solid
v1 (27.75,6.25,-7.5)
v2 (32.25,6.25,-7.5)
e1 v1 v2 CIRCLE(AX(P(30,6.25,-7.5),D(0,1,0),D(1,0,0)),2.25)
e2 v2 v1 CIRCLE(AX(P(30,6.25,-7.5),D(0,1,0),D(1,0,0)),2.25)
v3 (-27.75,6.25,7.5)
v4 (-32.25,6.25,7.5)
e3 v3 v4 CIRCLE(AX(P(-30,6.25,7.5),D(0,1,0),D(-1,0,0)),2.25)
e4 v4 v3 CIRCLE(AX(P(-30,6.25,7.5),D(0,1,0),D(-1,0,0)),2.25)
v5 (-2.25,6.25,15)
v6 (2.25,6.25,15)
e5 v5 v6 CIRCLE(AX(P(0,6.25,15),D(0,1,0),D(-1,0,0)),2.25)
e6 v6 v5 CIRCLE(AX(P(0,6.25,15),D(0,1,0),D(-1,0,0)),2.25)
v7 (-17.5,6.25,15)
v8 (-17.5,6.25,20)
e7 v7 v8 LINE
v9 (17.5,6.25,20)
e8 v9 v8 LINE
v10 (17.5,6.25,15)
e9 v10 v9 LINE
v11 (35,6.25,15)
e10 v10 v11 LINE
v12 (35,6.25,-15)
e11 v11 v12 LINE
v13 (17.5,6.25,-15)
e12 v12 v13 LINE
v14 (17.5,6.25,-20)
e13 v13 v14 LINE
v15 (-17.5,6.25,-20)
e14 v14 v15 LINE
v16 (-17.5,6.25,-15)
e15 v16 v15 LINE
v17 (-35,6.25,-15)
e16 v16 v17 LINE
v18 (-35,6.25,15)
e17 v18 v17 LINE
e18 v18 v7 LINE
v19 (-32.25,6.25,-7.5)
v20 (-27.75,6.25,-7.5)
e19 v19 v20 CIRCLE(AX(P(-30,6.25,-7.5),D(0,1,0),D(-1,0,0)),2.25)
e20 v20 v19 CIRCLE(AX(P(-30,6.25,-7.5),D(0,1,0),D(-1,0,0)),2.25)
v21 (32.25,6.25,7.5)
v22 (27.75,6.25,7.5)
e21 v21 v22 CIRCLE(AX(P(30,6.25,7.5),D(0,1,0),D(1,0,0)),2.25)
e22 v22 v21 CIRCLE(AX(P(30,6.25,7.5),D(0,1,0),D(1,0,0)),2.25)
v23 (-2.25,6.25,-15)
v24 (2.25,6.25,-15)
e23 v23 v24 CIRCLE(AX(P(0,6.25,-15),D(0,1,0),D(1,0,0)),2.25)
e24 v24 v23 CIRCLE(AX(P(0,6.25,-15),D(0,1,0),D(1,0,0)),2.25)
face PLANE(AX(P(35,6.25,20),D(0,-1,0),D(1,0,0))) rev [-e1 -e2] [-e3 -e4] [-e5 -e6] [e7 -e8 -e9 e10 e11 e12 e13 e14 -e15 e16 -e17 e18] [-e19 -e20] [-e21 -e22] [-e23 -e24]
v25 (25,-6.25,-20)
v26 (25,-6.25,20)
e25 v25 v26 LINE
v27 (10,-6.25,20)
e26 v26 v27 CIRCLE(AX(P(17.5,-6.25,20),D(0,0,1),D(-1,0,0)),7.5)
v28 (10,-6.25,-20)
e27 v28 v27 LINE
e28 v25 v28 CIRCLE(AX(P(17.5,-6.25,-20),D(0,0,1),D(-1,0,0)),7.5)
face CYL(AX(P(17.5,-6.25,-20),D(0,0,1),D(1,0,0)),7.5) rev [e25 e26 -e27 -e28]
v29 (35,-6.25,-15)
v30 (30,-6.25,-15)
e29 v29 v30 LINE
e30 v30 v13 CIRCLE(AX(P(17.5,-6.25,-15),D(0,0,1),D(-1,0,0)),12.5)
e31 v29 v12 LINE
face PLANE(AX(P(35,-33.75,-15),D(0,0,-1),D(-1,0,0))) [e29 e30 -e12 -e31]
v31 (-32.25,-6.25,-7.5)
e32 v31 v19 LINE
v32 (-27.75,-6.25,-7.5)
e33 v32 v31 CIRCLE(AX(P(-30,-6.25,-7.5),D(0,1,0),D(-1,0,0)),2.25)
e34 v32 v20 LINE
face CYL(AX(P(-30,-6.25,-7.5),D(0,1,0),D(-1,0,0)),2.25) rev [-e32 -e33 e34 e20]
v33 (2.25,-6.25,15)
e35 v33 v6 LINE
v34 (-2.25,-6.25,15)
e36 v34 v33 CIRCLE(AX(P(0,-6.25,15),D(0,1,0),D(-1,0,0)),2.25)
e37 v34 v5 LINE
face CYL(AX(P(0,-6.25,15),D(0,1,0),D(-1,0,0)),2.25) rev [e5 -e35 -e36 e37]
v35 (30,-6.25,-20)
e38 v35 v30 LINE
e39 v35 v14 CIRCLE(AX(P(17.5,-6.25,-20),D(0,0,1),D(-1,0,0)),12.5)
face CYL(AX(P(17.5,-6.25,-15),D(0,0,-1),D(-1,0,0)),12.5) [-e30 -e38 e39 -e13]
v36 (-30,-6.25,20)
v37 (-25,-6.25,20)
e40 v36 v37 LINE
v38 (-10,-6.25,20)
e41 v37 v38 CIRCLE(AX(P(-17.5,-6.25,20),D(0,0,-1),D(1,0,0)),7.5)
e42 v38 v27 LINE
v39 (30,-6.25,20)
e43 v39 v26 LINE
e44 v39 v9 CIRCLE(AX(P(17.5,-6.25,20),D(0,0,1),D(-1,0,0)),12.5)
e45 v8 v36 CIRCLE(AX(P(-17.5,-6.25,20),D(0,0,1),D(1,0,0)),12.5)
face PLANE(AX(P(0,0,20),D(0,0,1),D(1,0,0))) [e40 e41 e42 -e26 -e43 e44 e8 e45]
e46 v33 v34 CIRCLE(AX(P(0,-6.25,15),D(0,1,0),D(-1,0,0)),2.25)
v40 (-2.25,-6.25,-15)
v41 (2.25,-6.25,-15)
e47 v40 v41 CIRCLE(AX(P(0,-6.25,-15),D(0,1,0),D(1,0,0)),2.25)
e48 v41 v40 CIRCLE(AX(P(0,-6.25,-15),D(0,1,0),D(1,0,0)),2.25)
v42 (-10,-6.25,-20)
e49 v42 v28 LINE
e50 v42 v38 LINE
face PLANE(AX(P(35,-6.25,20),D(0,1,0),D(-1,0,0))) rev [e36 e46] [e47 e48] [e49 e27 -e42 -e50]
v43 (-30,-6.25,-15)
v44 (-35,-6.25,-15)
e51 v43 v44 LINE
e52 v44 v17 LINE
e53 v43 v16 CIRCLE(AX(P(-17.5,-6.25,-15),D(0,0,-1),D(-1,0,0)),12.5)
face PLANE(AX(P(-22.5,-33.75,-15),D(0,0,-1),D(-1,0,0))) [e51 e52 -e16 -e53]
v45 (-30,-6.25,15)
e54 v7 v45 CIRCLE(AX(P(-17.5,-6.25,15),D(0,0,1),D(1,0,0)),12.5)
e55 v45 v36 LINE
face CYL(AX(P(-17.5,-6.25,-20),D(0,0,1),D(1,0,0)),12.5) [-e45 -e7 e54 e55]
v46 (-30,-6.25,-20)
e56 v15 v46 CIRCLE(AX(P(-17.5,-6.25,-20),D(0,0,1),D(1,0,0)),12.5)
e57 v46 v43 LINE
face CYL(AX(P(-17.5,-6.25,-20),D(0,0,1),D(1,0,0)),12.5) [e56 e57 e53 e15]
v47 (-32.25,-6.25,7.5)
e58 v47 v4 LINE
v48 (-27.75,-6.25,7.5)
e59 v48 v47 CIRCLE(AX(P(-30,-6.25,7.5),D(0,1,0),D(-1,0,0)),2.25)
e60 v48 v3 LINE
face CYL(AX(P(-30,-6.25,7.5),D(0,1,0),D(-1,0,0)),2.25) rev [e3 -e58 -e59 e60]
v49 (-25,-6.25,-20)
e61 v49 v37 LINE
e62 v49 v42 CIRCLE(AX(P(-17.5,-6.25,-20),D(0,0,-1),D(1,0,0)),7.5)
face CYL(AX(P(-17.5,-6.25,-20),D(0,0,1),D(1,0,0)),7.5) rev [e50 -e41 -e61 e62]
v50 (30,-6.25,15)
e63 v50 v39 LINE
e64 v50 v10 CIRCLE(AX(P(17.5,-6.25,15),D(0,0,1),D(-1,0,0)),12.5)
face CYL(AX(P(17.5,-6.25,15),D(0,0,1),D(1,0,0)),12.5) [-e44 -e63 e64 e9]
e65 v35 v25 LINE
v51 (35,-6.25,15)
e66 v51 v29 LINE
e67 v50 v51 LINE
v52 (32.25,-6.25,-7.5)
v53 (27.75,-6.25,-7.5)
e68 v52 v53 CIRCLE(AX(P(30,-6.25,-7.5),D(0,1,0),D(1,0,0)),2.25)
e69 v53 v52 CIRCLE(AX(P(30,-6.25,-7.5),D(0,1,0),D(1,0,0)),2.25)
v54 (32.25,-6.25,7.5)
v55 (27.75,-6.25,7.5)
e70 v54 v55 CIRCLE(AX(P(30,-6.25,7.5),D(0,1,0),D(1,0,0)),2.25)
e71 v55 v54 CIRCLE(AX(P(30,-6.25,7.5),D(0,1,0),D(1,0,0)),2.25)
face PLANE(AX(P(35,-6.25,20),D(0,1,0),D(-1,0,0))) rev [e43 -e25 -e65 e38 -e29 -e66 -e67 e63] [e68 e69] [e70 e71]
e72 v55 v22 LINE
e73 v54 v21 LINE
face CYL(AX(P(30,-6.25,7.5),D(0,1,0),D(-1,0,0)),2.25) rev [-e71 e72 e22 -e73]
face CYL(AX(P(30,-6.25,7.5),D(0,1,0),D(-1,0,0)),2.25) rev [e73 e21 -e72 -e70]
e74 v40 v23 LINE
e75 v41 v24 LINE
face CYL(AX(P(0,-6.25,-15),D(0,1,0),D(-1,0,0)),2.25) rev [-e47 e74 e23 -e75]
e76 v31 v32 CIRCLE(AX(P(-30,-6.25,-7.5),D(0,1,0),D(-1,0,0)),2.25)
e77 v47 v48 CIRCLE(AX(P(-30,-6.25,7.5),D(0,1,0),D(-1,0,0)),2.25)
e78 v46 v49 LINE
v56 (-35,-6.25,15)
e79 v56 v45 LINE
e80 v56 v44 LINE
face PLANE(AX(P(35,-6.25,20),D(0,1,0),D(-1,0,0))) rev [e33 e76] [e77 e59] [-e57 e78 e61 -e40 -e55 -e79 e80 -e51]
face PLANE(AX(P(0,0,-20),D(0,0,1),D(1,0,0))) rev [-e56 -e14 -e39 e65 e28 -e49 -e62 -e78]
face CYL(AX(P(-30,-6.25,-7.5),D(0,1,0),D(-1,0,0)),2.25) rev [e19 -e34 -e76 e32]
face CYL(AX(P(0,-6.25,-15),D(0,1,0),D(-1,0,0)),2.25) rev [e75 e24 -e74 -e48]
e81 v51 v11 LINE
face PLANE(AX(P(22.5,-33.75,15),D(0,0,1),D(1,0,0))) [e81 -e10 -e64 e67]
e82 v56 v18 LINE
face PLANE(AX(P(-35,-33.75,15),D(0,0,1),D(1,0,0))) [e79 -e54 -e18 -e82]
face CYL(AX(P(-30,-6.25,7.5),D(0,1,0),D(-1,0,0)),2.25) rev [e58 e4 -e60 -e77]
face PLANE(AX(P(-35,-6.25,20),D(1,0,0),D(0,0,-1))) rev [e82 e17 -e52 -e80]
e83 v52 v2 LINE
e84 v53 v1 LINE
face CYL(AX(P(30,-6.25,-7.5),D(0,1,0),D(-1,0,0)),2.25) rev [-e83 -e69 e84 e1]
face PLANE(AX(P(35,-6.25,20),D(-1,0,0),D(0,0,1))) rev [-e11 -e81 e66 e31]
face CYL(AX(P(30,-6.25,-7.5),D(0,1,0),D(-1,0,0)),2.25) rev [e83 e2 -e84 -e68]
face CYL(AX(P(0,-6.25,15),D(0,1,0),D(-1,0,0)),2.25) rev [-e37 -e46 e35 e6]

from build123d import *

# Parameters (mm, degrees)
BASE_BLOCK_PROFILE_SKETCH_W            = 70
BASE_BLOCK_PROFILE_SKETCH_H            = 12.5
BASE_BLOCK_DEPTH                       = 20
SADDLE_CUTOUTS_SKETCH_OUTSIDE_W        = 88.318
SADDLE_CUTOUTS_SKETCH_OUTSIDE_H        = 58.318
SADDLE_CUTOUTS_DEPTH                   = 40
MOUNTING_HOLES_4_5_SKETCH_R            = 2.25
MOUNTING_HOLES_4_5_SET_A_DEPTH         = 43.20485754
COLLAR_BOSS_DEPTH                      = 40
COLLAR_BORE_CUT_DEPTH                  = 54.516936583
CORNER_NOTCH_DEPTH                     = 5
CORNER_NOTCH_MIRROR_RIGHT_COPY_1_DEPTH = 5
COLLAR_TRIM_CUT_DEPTH                  = 50.890505121
COLLAR_RELIEF_SKETCH_R                 = 7.5
COLLAR_RELIEF_CUT_DEPTH                = 54.516936583
SKETCH6_2_R                            = 2.25
MOUNTING_HOLES_4_5_SET_B_DEPTH         = 43.20485757


with BuildPart() as part:
    # Base Block Profile Sketch → Base Block (new, symmetric)
    with BuildSketch(Plane.XY):
        Rectangle(BASE_BLOCK_PROFILE_SKETCH_W, BASE_BLOCK_PROFILE_SKETCH_H)
    extrude(amount=BASE_BLOCK_DEPTH, both=True)

    # Saddle Cutouts Sketch outside → Saddle Cutouts (cut)
    with BuildSketch(Plane(origin=(0, 6.25, 0), x_dir=(1, 0, 0), z_dir=(0, 1, 0))):
        Rectangle(SADDLE_CUTOUTS_SKETCH_OUTSIDE_W, SADDLE_CUTOUTS_SKETCH_OUTSIDE_H)
        Polygon((-22.5, 20), (-22.5, 15), (-35, 15), (-35, -15), (-22.5, -15), (-22.5, -20), (22.5, -20), (22.5, -15), (35, -15), (35, 15), (22.5, 15), (22.5, 20), align=None, mode=Mode.SUBTRACT)
    extrude(amount=-SADDLE_CUTOUTS_DEPTH, mode=Mode.SUBTRACT)

    # Mounting Holes _4.5 Sketch → Mounting Holes _4.5 Set A (cut, through all)
    with BuildSketch(Plane(origin=(0, 6.25, 0), x_dir=(1, 0, 0), z_dir=(0, 1, 0))):
        with Locations(Location((-30, 7.5, 0), (0, 0, 180))):
            Circle(MOUNTING_HOLES_4_5_SKETCH_R)
        with Locations(Location((-30, -7.5, 0), (0, 0, 180))):
            Circle(MOUNTING_HOLES_4_5_SKETCH_R)
        with Locations((30, -7.5)):
            Circle(MOUNTING_HOLES_4_5_SKETCH_R)
        with Locations((30, 7.5)):
            Circle(MOUNTING_HOLES_4_5_SKETCH_R)
        with Locations(Location((0, -15, 0), (0, 0, 180))):
            Circle(MOUNTING_HOLES_4_5_SKETCH_R)
        with Locations((0, 15)):
            Circle(MOUNTING_HOLES_4_5_SKETCH_R)
    extrude(amount=-MOUNTING_HOLES_4_5_SET_A_DEPTH, mode=Mode.SUBTRACT)

    # Collar Boss Sketch → Collar Boss (add, through all)
    with BuildSketch(Plane.XY.offset(20)):
        with BuildLine():
            Line((-30, -6.25), (-25, -6.25))
            ThreePointArc((-25, -6.25), (-17.5, 1.25), (-10, -6.25))
            Line((-10, -6.25), (-5, -6.25))
            ThreePointArc((-5, -6.25), (-17.5, 6.25), (-30, -6.25))
        make_face()
    collar_boss = extrude(amount=-COLLAR_BOSS_DEPTH)

    # Sketch7_2 → Collar Bore Cut (cut, through all)
    with BuildSketch(Plane.XY.offset(20)):
        with BuildLine():
            ThreePointArc((-10, -6.25), (-14.438137822, 0.596531969), (-22.5, -0.659830056))
            Line((-22.5, -0.659830056), (-22.5, -6.25))
            Line((-22.5, -6.25), (-10, -6.25))
        make_face()
    extrude(amount=-COLLAR_BORE_CUT_DEPTH, mode=Mode.SUBTRACT)

    # Corner Notch Sketch → Corner Notch (cut)
    with BuildSketch(Plane.XY.offset(20)):
        with BuildLine():
            Line((-22.5, 5.206439237), (-22.5, 6.25))
            Line((-22.5, 6.25), (-17.5, 6.25))
            ThreePointArc((-17.5, 6.25), (-20.053870546, 5.986328912), (-22.5, 5.206439237))
        make_face()
    corner_notch = extrude(amount=-CORNER_NOTCH_DEPTH, mode=Mode.SUBTRACT)

    # Corner Notch Mirror Front: Corner Notch across plane
    add(corner_notch.mirror(Plane.XY), mode=Mode.SUBTRACT)

    # Corner Notch Mirror Right: Corner Notch across plane
    add(corner_notch.mirror(Plane(origin=(0, 0, 0), x_dir=(0, 0, 1), z_dir=(1, 0, 0))), mode=Mode.SUBTRACT)

    # Corner Notch Mirror Right copy 1 sketch → Corner Notch Mirror Right copy 1 (cut)
    with BuildSketch(Plane(origin=(0, 0, -20), x_dir=(-1, 0, 0), z_dir=(0, 0, -1))):
        with BuildLine():
            Line((-22.5, 5.206439237), (-22.5, 6.25))
            Line((-22.5, 6.25), (-17.5, 6.25))
            ThreePointArc((-17.5, 6.25), (-20.053870546, 5.986328912), (-22.5, 5.206439237))
        make_face()
    extrude(amount=-CORNER_NOTCH_MIRROR_RIGHT_COPY_1_DEPTH, mode=Mode.SUBTRACT)

    # Collar Boss Mirror: Collar Boss across plane
    add(collar_boss.mirror(Plane(origin=(0, 0, 0), x_dir=(0, 0, 1), z_dir=(1, 0, 0))))

    # Collar Trim Sketch → Collar Trim Cut (cut, through all)
    with BuildSketch(Plane.XY.offset(15)):
        with BuildLine():
            Line((-25, -6.25), (-22.5, -6.25))
            Line((-22.5, -6.25), (-22.5, -0.659830056))
            ThreePointArc((-22.5, -0.659830056), (-24.346531969, -3.188137822), (-25, -6.25))
        make_face()
    extrude(amount=-COLLAR_TRIM_CUT_DEPTH, mode=Mode.SUBTRACT)

    # Collar Relief Sketch → Collar Relief Cut (cut, through all)
    with BuildSketch(Plane.XY.offset(20)):
        with Locations((17.5, -6.25)):
            Circle(COLLAR_RELIEF_SKETCH_R)
    extrude(amount=-COLLAR_RELIEF_CUT_DEPTH, mode=Mode.SUBTRACT)

    # Sketch6_2 → Mounting Holes _4.5 Set B (cut, through all)
    with BuildSketch(Plane(origin=(0, 6.25, 0), x_dir=(1, 0, 0), z_dir=(0, 1, 0))):
        with Locations(Location((-30, 7.5, 0), (0, 0, 180))):
            Circle(SKETCH6_2_R)
        with Locations(Location((-30, -7.5, 0), (0, 0, 180))):
            Circle(SKETCH6_2_R)
        with Locations((30, -7.5)):
            Circle(SKETCH6_2_R)
        with Locations((30, 7.5)):
            Circle(SKETCH6_2_R)
        with Locations(Location((0, -15, 0), (0, 0, 180))):
            Circle(SKETCH6_2_R)
        with Locations((0, 15)):
            Circle(SKETCH6_2_R)
    extrude(amount=-MOUNTING_HOLES_4_5_SET_B_DEPTH, mode=Mode.SUBTRACT)


solid = part.part
